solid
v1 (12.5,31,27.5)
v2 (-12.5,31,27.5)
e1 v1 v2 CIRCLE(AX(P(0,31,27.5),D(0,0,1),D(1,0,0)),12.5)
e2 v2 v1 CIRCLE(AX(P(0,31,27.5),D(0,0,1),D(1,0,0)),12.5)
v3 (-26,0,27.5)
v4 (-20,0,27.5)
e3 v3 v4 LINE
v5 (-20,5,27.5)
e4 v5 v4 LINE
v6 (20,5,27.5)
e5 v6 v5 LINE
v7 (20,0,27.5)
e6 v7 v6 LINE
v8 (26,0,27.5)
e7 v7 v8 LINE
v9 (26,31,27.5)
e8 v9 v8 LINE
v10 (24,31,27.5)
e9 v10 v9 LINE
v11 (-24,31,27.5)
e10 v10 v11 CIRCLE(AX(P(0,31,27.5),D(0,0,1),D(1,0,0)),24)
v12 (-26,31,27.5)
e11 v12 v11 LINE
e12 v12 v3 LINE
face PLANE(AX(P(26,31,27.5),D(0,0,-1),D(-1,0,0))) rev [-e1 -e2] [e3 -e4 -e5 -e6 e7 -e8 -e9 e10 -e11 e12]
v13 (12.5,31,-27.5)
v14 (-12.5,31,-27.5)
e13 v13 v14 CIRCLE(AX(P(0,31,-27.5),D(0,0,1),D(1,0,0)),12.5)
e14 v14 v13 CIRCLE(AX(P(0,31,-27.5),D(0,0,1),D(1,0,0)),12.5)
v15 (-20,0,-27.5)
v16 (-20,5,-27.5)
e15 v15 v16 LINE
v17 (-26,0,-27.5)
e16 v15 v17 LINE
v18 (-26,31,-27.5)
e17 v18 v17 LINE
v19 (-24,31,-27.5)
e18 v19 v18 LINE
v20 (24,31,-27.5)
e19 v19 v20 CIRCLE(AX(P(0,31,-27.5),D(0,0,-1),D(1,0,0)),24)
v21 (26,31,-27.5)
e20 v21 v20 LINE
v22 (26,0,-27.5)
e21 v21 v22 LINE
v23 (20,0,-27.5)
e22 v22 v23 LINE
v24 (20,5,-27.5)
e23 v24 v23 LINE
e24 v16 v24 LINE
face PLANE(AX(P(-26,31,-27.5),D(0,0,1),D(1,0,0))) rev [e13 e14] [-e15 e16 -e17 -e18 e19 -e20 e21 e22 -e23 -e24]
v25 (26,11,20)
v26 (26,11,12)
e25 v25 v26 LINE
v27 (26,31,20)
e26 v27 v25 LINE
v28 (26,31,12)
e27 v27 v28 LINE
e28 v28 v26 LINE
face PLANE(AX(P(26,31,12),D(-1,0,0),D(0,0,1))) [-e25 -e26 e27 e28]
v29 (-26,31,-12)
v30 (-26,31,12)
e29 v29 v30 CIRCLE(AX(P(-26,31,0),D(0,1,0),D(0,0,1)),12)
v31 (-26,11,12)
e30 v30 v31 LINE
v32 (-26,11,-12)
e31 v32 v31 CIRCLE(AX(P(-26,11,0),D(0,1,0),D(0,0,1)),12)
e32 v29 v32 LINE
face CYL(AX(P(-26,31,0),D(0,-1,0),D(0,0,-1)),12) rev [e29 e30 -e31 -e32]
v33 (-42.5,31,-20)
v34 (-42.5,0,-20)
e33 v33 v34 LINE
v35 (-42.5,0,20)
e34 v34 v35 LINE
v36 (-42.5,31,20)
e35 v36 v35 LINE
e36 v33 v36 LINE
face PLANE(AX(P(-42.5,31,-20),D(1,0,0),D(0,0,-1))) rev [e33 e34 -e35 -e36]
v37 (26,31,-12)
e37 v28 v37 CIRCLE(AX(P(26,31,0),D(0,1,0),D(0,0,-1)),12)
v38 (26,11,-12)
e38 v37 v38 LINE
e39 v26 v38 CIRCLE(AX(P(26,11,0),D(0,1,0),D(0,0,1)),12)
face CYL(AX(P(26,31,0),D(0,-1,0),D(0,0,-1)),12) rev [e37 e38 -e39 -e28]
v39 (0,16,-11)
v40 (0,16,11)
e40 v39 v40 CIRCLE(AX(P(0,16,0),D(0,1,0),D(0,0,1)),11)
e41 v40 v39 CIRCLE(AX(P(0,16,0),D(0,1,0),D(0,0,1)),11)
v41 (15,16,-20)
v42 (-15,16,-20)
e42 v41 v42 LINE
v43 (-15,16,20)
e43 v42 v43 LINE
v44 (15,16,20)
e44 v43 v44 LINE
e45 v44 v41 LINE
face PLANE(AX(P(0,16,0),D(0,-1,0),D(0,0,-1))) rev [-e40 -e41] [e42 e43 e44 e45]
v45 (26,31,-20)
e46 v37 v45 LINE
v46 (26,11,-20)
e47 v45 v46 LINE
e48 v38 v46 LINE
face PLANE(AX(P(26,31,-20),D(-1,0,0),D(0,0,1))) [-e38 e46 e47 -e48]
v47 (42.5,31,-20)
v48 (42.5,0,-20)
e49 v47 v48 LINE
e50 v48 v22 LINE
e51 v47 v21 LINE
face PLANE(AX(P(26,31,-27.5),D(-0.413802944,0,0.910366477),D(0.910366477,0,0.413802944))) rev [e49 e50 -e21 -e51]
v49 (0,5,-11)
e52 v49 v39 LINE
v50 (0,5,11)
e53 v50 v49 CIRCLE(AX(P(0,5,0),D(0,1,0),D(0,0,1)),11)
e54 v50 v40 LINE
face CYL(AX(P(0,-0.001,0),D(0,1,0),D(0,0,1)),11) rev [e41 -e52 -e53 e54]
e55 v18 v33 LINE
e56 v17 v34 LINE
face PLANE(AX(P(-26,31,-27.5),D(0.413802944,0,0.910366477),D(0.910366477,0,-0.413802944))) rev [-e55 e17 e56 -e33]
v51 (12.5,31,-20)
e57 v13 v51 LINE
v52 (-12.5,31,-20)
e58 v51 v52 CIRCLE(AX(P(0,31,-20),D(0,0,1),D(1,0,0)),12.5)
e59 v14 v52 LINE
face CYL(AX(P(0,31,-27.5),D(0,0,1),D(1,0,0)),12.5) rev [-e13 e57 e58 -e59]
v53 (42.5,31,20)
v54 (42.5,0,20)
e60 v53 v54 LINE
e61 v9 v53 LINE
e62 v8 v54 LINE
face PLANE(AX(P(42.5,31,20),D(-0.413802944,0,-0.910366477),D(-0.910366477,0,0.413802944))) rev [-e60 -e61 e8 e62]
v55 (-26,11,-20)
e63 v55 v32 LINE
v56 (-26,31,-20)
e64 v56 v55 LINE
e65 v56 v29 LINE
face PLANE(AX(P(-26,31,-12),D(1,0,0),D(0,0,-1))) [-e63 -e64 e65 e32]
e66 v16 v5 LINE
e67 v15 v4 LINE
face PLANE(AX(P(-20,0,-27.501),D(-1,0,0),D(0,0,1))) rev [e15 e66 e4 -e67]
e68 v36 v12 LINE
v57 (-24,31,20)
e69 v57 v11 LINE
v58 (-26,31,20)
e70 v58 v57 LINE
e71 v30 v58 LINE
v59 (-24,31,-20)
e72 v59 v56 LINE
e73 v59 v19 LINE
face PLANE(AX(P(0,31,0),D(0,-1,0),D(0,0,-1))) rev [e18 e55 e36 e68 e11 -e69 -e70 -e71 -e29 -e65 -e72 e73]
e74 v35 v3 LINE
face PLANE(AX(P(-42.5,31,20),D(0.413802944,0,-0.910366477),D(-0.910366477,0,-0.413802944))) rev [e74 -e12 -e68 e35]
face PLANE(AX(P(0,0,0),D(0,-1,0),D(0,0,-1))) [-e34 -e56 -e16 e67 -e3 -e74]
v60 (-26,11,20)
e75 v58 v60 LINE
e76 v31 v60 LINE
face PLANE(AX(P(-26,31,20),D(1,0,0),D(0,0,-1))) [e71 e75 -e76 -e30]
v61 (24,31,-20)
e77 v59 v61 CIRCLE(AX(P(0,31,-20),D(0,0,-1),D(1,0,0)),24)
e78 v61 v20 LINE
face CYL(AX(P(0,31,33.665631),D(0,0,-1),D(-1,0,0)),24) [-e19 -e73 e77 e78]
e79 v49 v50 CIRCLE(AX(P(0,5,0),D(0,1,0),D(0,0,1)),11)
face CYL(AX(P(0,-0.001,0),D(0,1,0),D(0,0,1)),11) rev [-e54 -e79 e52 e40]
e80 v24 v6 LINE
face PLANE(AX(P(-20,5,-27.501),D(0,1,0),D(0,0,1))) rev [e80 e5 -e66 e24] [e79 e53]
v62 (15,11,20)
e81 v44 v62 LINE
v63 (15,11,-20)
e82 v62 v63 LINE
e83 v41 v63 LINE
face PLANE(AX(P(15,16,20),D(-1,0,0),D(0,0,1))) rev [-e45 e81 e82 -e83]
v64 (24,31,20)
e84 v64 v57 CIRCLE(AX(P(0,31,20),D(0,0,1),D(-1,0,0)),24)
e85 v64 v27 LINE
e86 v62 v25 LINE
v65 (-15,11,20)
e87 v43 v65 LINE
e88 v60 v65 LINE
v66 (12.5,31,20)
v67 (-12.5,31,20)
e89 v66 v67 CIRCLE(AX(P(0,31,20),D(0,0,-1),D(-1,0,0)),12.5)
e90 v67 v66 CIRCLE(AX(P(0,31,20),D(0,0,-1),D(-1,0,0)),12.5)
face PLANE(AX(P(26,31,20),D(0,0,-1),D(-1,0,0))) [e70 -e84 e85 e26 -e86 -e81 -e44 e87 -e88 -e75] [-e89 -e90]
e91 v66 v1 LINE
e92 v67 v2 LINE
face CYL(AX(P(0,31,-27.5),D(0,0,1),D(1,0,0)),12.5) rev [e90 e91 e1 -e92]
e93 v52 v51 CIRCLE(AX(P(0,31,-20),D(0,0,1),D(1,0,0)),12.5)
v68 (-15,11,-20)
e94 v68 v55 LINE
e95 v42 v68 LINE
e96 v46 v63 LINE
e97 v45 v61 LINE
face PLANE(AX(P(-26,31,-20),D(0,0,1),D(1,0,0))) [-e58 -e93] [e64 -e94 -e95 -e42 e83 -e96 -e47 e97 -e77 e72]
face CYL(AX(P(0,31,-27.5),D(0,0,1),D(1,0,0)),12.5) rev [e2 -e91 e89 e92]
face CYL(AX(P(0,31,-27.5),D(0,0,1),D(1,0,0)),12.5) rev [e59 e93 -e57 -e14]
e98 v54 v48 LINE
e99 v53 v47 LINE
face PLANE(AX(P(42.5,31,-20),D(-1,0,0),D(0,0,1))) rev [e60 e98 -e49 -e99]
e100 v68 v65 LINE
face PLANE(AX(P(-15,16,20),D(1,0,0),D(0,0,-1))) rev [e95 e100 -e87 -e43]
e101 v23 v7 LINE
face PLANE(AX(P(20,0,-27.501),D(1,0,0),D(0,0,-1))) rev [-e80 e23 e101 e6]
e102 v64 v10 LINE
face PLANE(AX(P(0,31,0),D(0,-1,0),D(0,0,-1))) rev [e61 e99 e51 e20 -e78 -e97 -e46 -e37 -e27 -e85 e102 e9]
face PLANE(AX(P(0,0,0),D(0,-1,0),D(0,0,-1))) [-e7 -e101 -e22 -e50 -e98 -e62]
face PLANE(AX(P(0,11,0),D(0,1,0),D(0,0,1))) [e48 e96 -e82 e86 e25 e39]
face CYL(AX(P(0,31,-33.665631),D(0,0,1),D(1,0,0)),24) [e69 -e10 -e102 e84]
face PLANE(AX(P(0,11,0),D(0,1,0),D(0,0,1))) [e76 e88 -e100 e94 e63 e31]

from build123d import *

# Parameters (mm, degrees)
BASE_BLOCK_DEPTH           = 31
LUG_A_DEPTH                = 7.5
LUG_START                  = -7.5
LUG_A_WEB_DEPTH            = 7.5
BORE_25_PROFILE_R          = 12.5
BORE_25_DEPTH              = 89.635489506
LUG_B_BASE_DEPTH           = 11
LUG_B_PROFILE_W            = 30
LUG_B_PROFILE_H            = 40
LUG_B_DEPTH                = 5
BORE_22_REACH              = 65.902
BORE_22_PROFILE_R          = 11
RELIEF_SLOT_40X5_REACH     = 90.635
RELIEF_SLOT_40X5_PROFILE_W = 40
RELIEF_SLOT_40X5_PROFILE_H = 5


with BuildPart() as part:
    # Base Block Profile → Base Block (new body)
    with BuildSketch(Plane(origin=(0, 0, 0), x_dir=(1, 0, 0), z_dir=(0, 1, 0))):
        Polygon((-26, 27.5), (26, 27.5), (42.5, 20), (42.5, -20), (26, -27.5), (-26, -27.5), (-42.5, -20), (-42.5, 20), align=None)
        with BuildLine():
            Line((-26, 20), (26, 20))
            Line((26, 20), (26, 12))
            ThreePointArc((26, 12), (38, 0), (26, -12))
            Line((26, -12), (26, -20))
            Line((26, -20), (-26, -20))
            Line((-26, -20), (-26, -12))
            ThreePointArc((-26, -12), (-38, 0), (-26, 12))
            Line((-26, 12), (-26, 20))
        make_face(mode=Mode.SUBTRACT)
    extrude(amount=BASE_BLOCK_DEPTH)

    # Lug A Profile → Lug A (add)
    with BuildSketch(Plane.XY.offset(27.5)):
        with BuildLine():
            Line((-24, 31), (24, 31))
            ThreePointArc((24, 31), (0, 55), (-24, 31))
        make_face()
    extrude(amount=-LUG_A_DEPTH)

    # Lug A Web Profile → Lug A Web (add)
    with BuildSketch(Plane(origin=(0, 0, -27.5), x_dir=(-1, 0, 0), z_dir=(0, 0, -1)).offset(LUG_START)):
        with BuildLine():
            Line((-24, 31), (24, 31))
            ThreePointArc((24, 31), (0, 55), (-24, 31))
        make_face()
    extrude(amount=LUG_A_WEB_DEPTH)

    # Bore _25 Profile → Bore _25 (cut, through all)
    with BuildSketch(Plane.XY.offset(27.5)):
        with Locations((0, 31)):
            Circle(BORE_25_PROFILE_R)
    extrude(amount=-BORE_25_DEPTH, mode=Mode.SUBTRACT)

    # Lug B Base Profile → Lug B Base (add)
    with BuildSketch(Plane(origin=(0, 0, 0), x_dir=(1, 0, 0), z_dir=(0, 1, 0))):
        Polygon((42.5, 20), (26, 27.5), (-26, 27.5), (-42.5, 20), (-42.5, -20), (-26, -27.5), (26, -27.5), (42.5, -20), align=None)
    extrude(amount=LUG_B_BASE_DEPTH)

    # Lug B Profile → Lug B (add)
    with BuildSketch(Plane(origin=(0, 11, 0), x_dir=(1, 0, 0), z_dir=(0, 1, 0))):
        Rectangle(LUG_B_PROFILE_W, LUG_B_PROFILE_H)
    extrude(amount=LUG_B_DEPTH)

    # Bore _22 Profile → Bore _22 (cut, up to next)
    with BuildSketch(Plane(origin=(0, 16, 0), x_dir=(1, 0, 0), z_dir=(0, 1, 0)), mode=Mode.PRIVATE) as bore_22_sk1:
        with Locations(Location((0, 0, 0), (0, 0, 270))):
            Circle(BORE_22_PROFILE_R)
    bore_22_tool1 = extrude(bore_22_sk1.sketch, amount=-BORE_22_REACH, mode=Mode.PRIVATE) & part.part
    add(bore_22_tool1.solids().sort_by_distance((0, 16, 0))[0], mode=Mode.SUBTRACT)

    # Relief Slot 40x5 Profile → Relief Slot 40x5 (cut, up to next)
    with BuildSketch(Plane.XY.offset(27.5), mode=Mode.PRIVATE) as relief_slot_40x5_sk1:
        with Locations((0, 2.5)):
            Rectangle(RELIEF_SLOT_40X5_PROFILE_W, RELIEF_SLOT_40X5_PROFILE_H)
    relief_slot_40x5_tool1 = extrude(relief_slot_40x5_sk1.sketch, amount=-RELIEF_SLOT_40X5_REACH, mode=Mode.PRIVATE) & part.part
    add(relief_slot_40x5_tool1.solids().sort_by_distance((0, 2.5, 27.5))[0], mode=Mode.SUBTRACT)


solid = part.part
